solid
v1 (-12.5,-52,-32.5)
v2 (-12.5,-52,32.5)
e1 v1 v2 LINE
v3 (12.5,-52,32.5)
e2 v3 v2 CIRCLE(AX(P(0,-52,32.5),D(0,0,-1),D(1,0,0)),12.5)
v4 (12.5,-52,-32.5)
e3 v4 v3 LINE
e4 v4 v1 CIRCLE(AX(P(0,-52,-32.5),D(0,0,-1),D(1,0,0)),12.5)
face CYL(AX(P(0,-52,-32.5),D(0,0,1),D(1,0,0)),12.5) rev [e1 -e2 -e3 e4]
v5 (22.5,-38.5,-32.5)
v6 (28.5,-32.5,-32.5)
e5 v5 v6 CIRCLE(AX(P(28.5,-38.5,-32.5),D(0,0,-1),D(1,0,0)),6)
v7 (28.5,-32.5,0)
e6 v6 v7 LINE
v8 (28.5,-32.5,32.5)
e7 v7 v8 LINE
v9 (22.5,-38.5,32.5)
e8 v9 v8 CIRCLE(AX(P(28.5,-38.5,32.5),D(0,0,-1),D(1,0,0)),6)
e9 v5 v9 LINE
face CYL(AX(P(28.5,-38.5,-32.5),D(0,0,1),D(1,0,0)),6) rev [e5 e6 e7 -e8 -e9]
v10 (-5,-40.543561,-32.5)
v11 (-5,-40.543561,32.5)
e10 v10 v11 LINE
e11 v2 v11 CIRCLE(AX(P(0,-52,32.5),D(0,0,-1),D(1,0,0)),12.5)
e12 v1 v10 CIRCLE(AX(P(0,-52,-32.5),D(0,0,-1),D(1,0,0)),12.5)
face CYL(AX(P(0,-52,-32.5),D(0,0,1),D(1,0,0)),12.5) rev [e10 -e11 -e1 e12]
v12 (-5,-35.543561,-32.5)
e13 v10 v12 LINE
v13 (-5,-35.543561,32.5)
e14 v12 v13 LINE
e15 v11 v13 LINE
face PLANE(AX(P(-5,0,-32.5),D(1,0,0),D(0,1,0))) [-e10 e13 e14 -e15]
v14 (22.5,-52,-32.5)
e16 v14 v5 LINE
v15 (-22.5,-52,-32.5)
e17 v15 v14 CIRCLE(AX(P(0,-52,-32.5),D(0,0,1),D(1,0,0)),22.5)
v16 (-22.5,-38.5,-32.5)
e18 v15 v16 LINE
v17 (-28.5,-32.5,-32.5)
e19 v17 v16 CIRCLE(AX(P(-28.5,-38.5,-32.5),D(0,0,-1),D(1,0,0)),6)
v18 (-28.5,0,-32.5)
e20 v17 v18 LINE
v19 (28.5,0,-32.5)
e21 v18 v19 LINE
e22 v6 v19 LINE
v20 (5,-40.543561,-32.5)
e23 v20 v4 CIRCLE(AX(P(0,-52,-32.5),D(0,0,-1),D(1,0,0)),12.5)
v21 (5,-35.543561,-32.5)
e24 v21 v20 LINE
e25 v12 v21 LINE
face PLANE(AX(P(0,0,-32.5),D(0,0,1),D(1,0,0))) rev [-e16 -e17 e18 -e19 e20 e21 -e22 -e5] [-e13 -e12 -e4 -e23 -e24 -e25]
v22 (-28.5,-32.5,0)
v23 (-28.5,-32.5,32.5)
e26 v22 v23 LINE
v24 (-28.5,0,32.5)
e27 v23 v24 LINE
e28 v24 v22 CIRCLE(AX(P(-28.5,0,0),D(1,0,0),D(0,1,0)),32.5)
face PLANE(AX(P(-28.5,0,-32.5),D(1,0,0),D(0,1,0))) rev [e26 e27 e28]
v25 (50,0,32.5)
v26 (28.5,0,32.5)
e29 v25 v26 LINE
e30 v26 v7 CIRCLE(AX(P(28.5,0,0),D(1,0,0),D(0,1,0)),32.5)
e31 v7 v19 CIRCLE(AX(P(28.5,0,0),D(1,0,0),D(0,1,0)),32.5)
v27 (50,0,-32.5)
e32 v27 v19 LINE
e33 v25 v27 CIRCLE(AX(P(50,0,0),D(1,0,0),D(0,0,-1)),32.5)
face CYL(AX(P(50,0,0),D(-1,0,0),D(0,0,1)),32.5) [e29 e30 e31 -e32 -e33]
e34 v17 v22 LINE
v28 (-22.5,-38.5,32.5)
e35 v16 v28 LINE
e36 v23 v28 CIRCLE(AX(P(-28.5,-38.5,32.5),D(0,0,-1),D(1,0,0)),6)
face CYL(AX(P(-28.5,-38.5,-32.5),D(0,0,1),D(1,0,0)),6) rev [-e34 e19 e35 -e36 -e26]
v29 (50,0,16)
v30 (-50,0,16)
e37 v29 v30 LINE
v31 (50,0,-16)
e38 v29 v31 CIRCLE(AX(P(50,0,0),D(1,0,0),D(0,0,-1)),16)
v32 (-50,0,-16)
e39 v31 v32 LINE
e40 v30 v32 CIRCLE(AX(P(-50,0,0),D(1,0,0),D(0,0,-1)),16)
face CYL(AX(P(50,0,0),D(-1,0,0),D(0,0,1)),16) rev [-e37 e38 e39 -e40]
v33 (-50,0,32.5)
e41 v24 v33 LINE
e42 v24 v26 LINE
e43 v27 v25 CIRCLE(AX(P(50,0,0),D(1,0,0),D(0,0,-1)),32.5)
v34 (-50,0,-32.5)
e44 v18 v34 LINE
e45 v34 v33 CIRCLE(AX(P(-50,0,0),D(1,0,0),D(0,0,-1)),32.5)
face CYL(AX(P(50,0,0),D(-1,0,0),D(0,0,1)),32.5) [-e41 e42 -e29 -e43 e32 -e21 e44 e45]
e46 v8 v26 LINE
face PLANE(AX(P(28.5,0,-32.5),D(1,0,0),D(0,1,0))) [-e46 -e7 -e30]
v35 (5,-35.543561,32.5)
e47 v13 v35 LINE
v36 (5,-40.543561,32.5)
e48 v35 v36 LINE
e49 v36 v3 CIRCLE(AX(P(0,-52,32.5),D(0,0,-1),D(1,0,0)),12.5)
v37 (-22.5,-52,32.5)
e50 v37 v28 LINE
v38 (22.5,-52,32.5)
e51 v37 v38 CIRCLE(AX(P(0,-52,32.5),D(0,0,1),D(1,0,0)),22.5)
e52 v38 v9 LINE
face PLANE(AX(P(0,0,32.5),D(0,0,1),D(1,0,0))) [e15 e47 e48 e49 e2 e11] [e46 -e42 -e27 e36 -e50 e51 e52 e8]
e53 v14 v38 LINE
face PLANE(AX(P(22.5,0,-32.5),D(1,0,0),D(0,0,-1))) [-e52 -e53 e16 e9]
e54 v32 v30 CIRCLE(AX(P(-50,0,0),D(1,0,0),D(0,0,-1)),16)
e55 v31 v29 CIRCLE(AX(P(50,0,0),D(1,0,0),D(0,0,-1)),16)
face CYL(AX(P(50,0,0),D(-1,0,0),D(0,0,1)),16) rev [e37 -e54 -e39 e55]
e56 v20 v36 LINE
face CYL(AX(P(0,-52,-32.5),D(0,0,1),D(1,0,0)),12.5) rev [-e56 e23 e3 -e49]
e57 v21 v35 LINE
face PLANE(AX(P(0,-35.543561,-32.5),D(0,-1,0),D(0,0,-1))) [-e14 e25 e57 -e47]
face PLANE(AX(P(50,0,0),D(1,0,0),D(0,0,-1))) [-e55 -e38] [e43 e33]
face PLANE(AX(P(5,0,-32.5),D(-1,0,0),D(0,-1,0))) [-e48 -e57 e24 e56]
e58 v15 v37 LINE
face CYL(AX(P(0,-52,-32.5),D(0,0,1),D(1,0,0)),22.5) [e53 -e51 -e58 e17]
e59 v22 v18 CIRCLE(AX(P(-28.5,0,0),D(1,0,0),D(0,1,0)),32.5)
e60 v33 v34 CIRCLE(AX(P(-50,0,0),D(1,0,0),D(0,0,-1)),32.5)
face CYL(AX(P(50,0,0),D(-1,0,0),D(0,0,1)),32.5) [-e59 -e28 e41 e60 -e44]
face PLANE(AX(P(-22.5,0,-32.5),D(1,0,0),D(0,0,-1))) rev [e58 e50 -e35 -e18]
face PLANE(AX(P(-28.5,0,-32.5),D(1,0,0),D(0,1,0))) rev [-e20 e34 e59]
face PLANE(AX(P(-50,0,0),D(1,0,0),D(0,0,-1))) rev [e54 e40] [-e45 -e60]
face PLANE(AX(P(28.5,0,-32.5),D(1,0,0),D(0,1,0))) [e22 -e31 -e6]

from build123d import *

# Parameters (mm, degrees)
SLEEVE_PROFILE_65_32_R   = 32.5
SLEEVE_PROFILE_65_32_R_2 = 16
SLEEVE_65X100_DEPTH      = 50
BRACKET_WEB_DEPTH        = 32.5
SIDE_RAILS_DEPTH         = 65
LUG_START                = -255
LUG_HOLE_PROFILE_R       = 16
LUG_HOLE_THROUGH_DEPTH   = 255


with BuildPart() as part:
    # Sleeve Profile Ø65-Ø32 → Sleeve Ø65x100 (new, symmetric)
    with BuildSketch(Plane(origin=(0, 0, 0), x_dir=(0, 0, -1), z_dir=(1, 0, 0))):
        Circle(SLEEVE_PROFILE_65_32_R)
        Circle(SLEEVE_PROFILE_65_32_R_2, mode=Mode.SUBTRACT)
    extrude(amount=SLEEVE_65X100_DEPTH, both=True)



with BuildPart() as body_2:
    # Bracket Web Profile → Bracket Web (new, symmetric)
    with BuildSketch(Plane.XY):
        with BuildLine():
            Line((0, -32.5), (-28.5, -32.5))
            ThreePointArc((-28.5, -32.5), (-24.257359313, -34.257359313), (-22.5, -38.5))
            Line((-22.5, -38.5), (-22.5, -52))
            ThreePointArc((-22.5, -52), (0, -74.5), (22.5, -52))
            Line((22.5, -52), (22.5, -38.5))
            ThreePointArc((22.5, -38.5), (24.257359313, -34.257359313), (28.5, -32.5))
            Line((28.5, -32.5), (0, -32.5))
        make_face()
        with BuildLine():
            Line((-5, -35.543560763), (0, -35.543560763))
            Line((0, -35.543560763), (5, -35.543560763))
            Line((5, -35.543560763), (5, -40.543560763))
            ThreePointArc((5, -40.543560763), (0, -64.5), (-5, -40.543560763))
            Line((-5, -40.543560763), (-5, -35.543560763))
        make_face(mode=Mode.SUBTRACT)
    extrude(amount=BRACKET_WEB_DEPTH, both=True)


with BuildPart() as part_1:
    add(part.part)

    add(body_2.part)  # Side Rails merges body 2
    # Side Rail Profile → Side Rails (add)
    # profile 1 of 9: a face of its own
    with BuildSketch(Plane.XY.offset(32.5)):
        with BuildLine():
            Line((-22.5, -32.5), (-28.5, -32.5))
            ThreePointArc((-28.5, -32.5), (-24.257359313, -34.257359313), (-22.5, -38.5))
            Line((-22.5, -38.5), (-22.5, -32.5))
        make_face()
    # profile 2 of 9: a face of its own
    with BuildSketch(Plane.XY.offset(32.5)):
        with BuildLine():
            Line((-23.44711749, -7.891120858), (-28.5, 0))
            Line((-28.5, 0), (-28.5, -32.5))
            Line((-28.5, -32.5), (-22.5, -32.5))
            Line((-22.5, -32.5), (-22.5, -11.126608201))
            ThreePointArc((-22.5, -11.126608201), (-22.741645415, -9.440977022), (-23.44711749, -7.891120858))
        make_face()
    # profile 3 of 9: a face of its own
    with BuildSketch(Plane.XY.offset(32.5)):
        with BuildLine():
            Line((28.5, 0), (-28.5, 0))
            Line((-28.5, 0), (-23.44711749, -7.891120858))
            ThreePointArc((-23.44711749, -7.891120858), (-22.741645415, -9.440977022), (-22.5, -11.126608201))
            Line((-22.5, -11.126608201), (-22.5, -32.5))
            Line((-22.5, -32.5), (-11.22497216, -32.5))
            ThreePointArc((-11.22497216, -32.5), (0, -29.5), (11.22497216, -32.5))
            Line((11.22497216, -32.5), (22.5, -32.5))
            Line((22.5, -32.5), (22.5, -11.126608201))
            ThreePointArc((22.5, -11.126608201), (22.741645415, -9.440977022), (23.44711749, -7.891120858))
            Line((23.44711749, -7.891120858), (28.5, 0))
        make_face()
    # profile 4 of 9: a face of its own
    with BuildSketch(Plane.XY.offset(32.5)):
        with BuildLine():
            Line((28.5, -32.5), (28.5, 0))
            Line((28.5, 0), (23.44711749, -7.891120858))
            ThreePointArc((23.44711749, -7.891120858), (22.741645415, -9.440977022), (22.5, -11.126608201))
            Line((22.5, -11.126608201), (22.5, -32.5))
            Line((22.5, -32.5), (28.5, -32.5))
        make_face()
    # profile 5 of 9: a face of its own
    with BuildSketch(Plane.XY.offset(32.5)):
        with BuildLine():
            Line((22.5, -52), (22.5, -38.5))
            Line((22.5, -38.5), (22.5, -32.5))
            Line((22.5, -32.5), (11.22497216, -32.5))
            ThreePointArc((11.22497216, -32.5), (19.47834533, -40.737493032), (22.5, -52))
        make_face()
    # profile 6 of 9: a face of its own
    with BuildSketch(Plane.XY.offset(32.5)):
        with BuildLine():
            ThreePointArc((22.5, -38.5), (24.257359313, -34.257359313), (28.5, -32.5))
            Line((28.5, -32.5), (22.5, -32.5))
            Line((22.5, -32.5), (22.5, -38.5))
        make_face()
    # profile 7 of 9: a face of its own
    with BuildSketch(Plane.XY.offset(32.5)):
        with BuildLine():
            Line((-22.5, -32.5), (-22.5, -38.5))
            Line((-22.5, -38.5), (-22.5, -52))
            ThreePointArc((-22.5, -52), (-19.47834533, -40.737493032), (-11.22497216, -32.5))
            Line((-11.22497216, -32.5), (-22.5, -32.5))
        make_face()
    # profile 8 of 9: a face of its own
    with BuildSketch(Plane.XY.offset(32.5)):
        with BuildLine():
            ThreePointArc((-11.22497216, -32.5), (-19.47834533, -40.737493032), (-22.5, -52))
            ThreePointArc((-22.5, -52), (0, -74.5), (22.5, -52))
            ThreePointArc((22.5, -52), (19.47834533, -40.737493032), (11.22497216, -32.5))
            Line((11.22497216, -32.5), (-11.22497216, -32.5))
        make_face()
        with BuildLine():
            ThreePointArc((5, -40.543560763), (0, -64.5), (-5, -40.543560763))
            Line((-5, -40.543560763), (-5, -35.543560763))
            Line((-5, -35.543560763), (5, -35.543560763))
            Line((5, -35.543560763), (5, -40.543560763))
        make_face(mode=Mode.SUBTRACT)
    # profile 9 of 9: a face of its own
    with BuildSketch(Plane.XY.offset(32.5)):
        with BuildLine():
            ThreePointArc((11.22497216, -32.5), (0, -29.5), (-11.22497216, -32.5))
            Line((-11.22497216, -32.5), (11.22497216, -32.5))
        make_face()
    extrude(amount=-SIDE_RAILS_DEPTH)

    # Lug Hole Profile → Lug Hole Through (cut)
    with BuildSketch(Plane(origin=(50, 0, 0), x_dir=(0, 0, -1), z_dir=(1, 0, 0)).offset(LUG_START)):
        Circle(LUG_HOLE_PROFILE_R)
    extrude(amount=LUG_HOLE_THROUGH_DEPTH, mode=Mode.SUBTRACT)


solid = part_1.part
